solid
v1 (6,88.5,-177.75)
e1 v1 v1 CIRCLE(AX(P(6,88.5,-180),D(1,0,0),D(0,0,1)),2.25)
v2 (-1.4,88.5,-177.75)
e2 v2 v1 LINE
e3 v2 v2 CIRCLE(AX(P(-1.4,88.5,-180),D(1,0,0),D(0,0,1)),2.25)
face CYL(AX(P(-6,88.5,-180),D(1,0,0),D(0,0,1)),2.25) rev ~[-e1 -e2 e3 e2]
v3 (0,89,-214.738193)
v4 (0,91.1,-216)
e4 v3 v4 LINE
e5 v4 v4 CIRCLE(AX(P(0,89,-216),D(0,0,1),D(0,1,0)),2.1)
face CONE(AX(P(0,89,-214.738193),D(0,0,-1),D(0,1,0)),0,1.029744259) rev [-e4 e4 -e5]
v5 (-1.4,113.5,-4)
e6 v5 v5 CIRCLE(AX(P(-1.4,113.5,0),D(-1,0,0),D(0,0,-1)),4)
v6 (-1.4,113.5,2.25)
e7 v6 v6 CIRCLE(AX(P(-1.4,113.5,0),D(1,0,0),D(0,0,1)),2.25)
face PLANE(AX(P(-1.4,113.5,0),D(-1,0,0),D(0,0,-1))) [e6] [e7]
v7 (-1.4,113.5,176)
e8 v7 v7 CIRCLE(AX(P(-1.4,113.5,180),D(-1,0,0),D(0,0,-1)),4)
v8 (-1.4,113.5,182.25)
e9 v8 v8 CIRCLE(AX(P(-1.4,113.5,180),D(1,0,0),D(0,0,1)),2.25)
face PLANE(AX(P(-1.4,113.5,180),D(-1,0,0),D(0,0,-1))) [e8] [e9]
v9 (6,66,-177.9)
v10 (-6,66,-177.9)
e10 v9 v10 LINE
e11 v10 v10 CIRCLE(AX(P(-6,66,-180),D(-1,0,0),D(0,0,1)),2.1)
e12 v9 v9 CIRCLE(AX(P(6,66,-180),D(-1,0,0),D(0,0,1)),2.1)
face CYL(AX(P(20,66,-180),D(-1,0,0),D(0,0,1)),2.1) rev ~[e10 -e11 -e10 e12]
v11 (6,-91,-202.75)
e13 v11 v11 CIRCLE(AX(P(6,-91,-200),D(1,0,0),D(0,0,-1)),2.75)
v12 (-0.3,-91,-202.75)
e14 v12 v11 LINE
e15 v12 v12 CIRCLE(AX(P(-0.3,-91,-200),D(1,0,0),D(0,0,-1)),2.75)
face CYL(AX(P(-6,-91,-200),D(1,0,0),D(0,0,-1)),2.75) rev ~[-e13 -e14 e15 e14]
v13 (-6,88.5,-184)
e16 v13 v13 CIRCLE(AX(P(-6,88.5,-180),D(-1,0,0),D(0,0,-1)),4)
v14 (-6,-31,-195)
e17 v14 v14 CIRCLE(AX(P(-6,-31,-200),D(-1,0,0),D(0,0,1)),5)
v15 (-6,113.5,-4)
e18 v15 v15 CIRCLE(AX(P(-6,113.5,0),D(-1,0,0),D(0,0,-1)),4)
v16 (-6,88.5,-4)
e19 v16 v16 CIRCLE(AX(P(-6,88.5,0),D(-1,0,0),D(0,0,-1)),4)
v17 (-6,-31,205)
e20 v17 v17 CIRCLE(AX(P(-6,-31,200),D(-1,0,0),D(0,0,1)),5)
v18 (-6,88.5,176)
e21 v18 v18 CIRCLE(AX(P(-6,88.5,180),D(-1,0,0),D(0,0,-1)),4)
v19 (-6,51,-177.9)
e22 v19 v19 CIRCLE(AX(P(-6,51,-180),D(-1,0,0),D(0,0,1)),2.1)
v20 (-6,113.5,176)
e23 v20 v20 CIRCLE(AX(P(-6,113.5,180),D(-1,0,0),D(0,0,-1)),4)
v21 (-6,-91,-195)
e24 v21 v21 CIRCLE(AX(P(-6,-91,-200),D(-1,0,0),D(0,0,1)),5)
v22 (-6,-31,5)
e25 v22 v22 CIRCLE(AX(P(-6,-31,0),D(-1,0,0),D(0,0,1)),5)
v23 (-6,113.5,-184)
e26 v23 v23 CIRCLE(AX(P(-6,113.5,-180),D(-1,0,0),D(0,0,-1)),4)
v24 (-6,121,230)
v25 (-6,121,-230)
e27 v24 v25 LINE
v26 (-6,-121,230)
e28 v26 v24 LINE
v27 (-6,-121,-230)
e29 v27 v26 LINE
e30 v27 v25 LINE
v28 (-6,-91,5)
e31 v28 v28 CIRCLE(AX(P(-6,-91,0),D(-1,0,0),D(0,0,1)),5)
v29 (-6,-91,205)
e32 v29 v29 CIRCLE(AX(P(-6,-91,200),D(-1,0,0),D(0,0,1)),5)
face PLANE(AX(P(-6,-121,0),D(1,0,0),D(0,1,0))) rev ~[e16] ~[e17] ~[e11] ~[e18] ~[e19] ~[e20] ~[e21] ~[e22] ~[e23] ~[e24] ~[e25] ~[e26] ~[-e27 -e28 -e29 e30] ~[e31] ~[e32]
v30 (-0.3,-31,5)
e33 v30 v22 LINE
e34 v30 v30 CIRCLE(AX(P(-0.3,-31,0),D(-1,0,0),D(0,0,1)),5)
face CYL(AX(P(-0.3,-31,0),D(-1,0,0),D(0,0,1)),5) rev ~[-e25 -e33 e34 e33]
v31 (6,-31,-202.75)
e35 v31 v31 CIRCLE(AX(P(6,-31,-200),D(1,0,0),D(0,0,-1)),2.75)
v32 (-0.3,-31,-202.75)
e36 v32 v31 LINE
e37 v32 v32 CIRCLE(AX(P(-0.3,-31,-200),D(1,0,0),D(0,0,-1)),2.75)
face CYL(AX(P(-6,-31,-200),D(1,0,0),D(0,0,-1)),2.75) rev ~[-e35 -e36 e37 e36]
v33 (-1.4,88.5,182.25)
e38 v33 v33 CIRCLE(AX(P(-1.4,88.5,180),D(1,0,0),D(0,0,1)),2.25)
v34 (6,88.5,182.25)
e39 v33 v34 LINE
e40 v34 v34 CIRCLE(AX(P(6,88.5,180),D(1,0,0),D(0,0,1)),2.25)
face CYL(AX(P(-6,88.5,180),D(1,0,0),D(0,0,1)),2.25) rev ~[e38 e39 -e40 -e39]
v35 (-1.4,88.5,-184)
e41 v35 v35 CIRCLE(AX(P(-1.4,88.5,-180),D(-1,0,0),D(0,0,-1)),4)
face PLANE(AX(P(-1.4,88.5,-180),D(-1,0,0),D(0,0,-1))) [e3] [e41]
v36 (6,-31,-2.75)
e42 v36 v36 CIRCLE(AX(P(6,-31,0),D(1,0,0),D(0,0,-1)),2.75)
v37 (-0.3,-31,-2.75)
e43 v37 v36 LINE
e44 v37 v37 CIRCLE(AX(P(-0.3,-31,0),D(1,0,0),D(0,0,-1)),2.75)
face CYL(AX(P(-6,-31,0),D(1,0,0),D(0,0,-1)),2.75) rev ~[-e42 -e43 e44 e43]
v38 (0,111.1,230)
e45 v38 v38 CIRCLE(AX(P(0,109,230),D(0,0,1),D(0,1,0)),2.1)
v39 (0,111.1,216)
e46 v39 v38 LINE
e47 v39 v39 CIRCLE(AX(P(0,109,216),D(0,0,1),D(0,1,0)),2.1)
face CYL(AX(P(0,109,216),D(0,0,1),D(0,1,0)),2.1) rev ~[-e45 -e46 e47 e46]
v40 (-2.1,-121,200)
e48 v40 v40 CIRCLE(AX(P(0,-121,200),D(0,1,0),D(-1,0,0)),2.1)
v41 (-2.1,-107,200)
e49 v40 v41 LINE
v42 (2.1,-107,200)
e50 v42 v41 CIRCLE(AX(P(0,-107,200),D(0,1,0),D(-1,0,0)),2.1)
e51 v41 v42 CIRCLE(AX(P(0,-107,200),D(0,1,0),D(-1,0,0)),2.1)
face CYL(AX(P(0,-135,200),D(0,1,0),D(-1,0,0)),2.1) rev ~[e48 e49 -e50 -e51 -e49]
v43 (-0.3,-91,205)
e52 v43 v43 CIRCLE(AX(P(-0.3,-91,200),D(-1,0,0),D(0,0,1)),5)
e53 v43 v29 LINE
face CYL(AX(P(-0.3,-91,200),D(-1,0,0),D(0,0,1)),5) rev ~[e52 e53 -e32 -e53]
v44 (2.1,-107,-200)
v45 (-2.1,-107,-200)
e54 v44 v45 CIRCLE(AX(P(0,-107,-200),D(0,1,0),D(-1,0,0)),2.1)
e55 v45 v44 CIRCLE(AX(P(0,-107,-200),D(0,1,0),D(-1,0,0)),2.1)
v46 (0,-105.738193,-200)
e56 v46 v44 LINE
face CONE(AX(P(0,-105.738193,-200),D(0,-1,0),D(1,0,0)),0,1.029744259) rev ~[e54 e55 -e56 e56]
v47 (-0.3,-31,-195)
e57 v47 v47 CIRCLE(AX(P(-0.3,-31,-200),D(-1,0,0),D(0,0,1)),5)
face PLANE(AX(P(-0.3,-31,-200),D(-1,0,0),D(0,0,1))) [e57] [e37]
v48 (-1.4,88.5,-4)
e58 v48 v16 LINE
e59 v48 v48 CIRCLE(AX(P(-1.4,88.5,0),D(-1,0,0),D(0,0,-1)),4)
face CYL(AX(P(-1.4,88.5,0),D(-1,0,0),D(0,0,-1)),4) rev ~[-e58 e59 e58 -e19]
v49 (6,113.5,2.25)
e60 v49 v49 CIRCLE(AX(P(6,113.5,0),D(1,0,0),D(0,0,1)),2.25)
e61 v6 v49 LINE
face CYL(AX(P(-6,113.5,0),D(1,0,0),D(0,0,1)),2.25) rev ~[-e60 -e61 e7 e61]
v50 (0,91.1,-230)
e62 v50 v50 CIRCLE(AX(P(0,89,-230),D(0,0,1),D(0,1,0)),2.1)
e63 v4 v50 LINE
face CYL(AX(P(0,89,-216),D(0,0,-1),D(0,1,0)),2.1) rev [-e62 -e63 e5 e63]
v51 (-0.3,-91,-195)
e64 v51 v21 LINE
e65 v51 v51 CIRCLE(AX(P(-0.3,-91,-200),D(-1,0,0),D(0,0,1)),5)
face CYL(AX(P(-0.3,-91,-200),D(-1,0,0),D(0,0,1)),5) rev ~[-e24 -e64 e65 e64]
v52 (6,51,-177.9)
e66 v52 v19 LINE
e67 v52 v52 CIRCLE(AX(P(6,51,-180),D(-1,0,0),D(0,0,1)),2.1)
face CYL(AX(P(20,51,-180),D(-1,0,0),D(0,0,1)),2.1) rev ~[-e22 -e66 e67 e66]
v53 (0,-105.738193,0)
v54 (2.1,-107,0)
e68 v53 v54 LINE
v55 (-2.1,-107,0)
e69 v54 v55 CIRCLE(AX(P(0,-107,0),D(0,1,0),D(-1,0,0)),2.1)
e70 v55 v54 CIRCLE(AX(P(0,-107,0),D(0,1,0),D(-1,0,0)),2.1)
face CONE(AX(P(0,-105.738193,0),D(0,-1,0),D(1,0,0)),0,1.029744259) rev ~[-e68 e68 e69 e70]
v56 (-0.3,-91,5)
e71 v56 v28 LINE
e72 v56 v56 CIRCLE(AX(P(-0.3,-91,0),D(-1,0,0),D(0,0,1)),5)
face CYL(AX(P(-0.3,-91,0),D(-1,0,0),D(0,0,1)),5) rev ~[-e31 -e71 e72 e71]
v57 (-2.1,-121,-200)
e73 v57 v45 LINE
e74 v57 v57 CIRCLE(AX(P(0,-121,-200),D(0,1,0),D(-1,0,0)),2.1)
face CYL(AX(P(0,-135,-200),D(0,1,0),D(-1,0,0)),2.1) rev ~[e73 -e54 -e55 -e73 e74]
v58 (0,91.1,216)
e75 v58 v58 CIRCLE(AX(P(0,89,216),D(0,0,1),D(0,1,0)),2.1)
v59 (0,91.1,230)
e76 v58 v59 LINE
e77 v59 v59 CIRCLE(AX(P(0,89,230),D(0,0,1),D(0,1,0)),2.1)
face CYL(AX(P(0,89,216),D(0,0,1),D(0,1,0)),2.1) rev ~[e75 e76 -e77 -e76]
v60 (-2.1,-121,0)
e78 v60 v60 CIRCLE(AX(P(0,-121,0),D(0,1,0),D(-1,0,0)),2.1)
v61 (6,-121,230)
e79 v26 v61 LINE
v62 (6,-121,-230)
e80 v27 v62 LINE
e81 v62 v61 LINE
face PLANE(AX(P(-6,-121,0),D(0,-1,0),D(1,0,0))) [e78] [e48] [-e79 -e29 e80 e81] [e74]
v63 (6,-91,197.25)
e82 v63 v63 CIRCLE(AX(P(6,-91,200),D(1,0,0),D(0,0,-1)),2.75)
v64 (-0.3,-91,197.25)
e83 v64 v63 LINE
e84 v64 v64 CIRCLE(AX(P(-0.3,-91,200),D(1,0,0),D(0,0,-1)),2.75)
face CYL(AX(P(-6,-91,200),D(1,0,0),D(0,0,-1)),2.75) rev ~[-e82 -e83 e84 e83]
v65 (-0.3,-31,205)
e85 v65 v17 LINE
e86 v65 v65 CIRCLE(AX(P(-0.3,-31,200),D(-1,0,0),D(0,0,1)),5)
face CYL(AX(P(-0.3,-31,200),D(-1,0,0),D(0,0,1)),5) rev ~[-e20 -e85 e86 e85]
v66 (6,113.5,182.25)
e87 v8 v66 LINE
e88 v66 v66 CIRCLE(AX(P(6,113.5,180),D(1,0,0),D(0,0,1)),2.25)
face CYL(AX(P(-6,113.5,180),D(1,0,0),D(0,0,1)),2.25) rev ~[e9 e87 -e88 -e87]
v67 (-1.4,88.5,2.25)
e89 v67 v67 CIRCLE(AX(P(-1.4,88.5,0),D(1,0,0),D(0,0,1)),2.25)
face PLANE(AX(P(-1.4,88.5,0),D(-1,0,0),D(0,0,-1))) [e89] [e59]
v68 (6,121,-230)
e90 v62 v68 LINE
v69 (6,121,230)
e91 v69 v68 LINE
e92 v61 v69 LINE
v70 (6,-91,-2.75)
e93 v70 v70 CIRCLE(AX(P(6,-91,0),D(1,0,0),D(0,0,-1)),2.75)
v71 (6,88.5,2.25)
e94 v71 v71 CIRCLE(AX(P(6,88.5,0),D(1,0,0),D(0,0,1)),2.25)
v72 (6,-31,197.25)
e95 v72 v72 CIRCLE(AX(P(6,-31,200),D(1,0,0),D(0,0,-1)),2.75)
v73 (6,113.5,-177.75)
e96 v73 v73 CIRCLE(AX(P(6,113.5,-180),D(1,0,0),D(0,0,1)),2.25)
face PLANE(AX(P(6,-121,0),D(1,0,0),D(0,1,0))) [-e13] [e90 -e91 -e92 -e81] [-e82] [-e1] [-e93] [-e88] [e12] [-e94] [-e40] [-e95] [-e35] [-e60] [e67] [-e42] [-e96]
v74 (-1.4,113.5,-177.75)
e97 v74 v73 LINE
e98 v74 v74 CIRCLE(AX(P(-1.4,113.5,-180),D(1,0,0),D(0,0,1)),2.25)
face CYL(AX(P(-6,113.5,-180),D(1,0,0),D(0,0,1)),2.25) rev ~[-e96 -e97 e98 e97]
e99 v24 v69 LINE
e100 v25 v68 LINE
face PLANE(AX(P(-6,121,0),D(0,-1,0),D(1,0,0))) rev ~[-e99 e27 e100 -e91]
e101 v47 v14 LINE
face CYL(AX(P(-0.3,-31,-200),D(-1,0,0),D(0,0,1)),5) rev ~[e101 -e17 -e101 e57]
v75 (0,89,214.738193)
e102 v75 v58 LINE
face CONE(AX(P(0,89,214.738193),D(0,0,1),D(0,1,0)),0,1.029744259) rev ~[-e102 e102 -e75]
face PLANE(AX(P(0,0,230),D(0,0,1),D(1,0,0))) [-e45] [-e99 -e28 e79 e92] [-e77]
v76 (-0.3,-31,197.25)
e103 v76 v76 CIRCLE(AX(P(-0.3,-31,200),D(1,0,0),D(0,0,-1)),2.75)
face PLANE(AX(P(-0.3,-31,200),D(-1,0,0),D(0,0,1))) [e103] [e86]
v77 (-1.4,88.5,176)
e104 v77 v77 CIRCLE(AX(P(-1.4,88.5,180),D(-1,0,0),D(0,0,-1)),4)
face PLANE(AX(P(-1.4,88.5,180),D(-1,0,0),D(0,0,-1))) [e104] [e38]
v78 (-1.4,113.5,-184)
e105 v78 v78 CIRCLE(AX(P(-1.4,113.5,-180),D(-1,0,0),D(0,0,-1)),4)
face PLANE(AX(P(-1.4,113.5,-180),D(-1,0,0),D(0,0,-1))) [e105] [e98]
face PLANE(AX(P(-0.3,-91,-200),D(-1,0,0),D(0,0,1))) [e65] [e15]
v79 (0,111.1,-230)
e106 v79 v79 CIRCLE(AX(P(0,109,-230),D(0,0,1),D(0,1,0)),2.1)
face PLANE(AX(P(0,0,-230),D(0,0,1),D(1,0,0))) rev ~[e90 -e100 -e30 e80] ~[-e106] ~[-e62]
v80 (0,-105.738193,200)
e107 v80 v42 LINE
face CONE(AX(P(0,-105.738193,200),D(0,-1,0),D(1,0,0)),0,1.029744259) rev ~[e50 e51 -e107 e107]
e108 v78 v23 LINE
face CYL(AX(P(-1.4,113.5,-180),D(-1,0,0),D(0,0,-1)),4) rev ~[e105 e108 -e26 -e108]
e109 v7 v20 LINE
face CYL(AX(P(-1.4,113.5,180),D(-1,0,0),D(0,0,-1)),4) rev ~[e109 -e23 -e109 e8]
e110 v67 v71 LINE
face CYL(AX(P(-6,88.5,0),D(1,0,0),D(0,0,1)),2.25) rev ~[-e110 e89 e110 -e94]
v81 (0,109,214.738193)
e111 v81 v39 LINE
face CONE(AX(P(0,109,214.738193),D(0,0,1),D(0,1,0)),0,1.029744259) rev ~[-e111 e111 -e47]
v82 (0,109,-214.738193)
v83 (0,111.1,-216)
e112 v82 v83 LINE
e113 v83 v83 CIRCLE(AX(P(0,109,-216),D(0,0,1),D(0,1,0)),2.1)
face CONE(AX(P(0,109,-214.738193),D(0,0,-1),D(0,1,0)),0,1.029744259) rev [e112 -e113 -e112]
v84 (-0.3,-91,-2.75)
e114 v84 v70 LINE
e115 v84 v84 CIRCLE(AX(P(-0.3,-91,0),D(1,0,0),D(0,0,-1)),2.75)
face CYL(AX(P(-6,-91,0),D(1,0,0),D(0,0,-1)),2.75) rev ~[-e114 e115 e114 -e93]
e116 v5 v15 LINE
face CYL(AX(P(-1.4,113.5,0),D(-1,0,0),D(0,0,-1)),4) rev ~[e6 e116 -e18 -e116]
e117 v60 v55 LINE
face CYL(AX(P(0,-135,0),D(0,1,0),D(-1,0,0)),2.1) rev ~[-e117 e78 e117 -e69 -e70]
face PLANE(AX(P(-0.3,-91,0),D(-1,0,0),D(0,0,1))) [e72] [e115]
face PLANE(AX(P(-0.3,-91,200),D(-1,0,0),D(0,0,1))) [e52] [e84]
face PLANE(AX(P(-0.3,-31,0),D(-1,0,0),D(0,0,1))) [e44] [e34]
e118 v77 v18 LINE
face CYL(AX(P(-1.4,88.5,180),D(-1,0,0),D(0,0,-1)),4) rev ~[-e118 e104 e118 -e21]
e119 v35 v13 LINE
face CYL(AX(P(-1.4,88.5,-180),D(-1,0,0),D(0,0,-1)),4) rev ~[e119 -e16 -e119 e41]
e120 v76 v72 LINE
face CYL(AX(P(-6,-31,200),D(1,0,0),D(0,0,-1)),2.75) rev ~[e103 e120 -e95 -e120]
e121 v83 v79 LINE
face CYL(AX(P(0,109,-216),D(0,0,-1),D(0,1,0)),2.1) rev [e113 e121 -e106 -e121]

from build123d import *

# Parameters (mm, degrees)
SKETCH_1_W                  = 12
SKETCH_1_H                  = 242
EXTRUDE_1_DEPTH             = 230
HOLE_WIZARD_M5_1_D          = 4.2
HOLE_WIZARD_M5_1_DEPTH      = 14
HOLE_WIZARD_M5_1_TIP        = 1.2618073
HOLE_WIZARD_1_D             = 5.5
HOLE_WIZARD_1_DEPTH         = 14
HOLE_WIZARD_1_CBORE_D       = 10
HOLE_WIZARD_1_CBORE_DEPTH   = 5.7
HOLE_WIZARD_1_TIP           = 1.652366702
HOLE_WIZARD_2_D             = 4.5
HOLE_WIZARD_2_DEPTH         = 14
HOLE_WIZARD_2_CBORE_D       = 8
HOLE_WIZARD_2_CBORE_DEPTH   = 4.6
HOLE_WIZARD_2_TIP           = 1.351936393
HOLE_WIZARD_M5_2_AT_2_COUNT = 2
HOLE_WIZARD_M5_2_AT_2_PITCH = 20
HOLE_WIZARD_M5_3_D          = 4.2
HOLE_WIZARD_M5_3_DEPTH      = 14
HOLE_WIZARD_M5_3_TIP        = 1.2618073


with BuildPart() as part:
    # 草图1 → 凸台-拉伸1 (new, symmetric)
    with BuildSketch(Plane.XY):
        Rectangle(SKETCH_1_W, SKETCH_1_H)
    extrude(amount=EXTRUDE_1_DEPTH, both=True)

    # M5 螺纹孔1
    with Locations(Plane.XZ.offset(121)):
        with Locations((0, 200), (0, 0), (0, -200)):
            Hole(HOLE_WIZARD_M5_1_D / 2, depth=HOLE_WIZARD_M5_1_DEPTH)
            with Locations((0, 0, -(HOLE_WIZARD_M5_1_DEPTH + HOLE_WIZARD_M5_1_TIP / 2))):  # 118° drill point
                Cone(0, HOLE_WIZARD_M5_1_D / 2, HOLE_WIZARD_M5_1_TIP, mode=Mode.SUBTRACT)

    # 打孔尺寸(%根据)内六角圆柱头螺钉的类型1
    with Locations(Plane.ZY.offset(6)):
        with Locations((200, -31), (200, -91), (0, -31), (0, -91), (-200, -31), (-200, -91)):
            CounterBoreHole(HOLE_WIZARD_1_D / 2, HOLE_WIZARD_1_CBORE_D / 2, HOLE_WIZARD_1_CBORE_DEPTH, depth=HOLE_WIZARD_1_DEPTH)
            with Locations((0, 0, -(HOLE_WIZARD_1_DEPTH + HOLE_WIZARD_1_TIP / 2))):  # 118° drill point
                Cone(0, HOLE_WIZARD_1_D / 2, HOLE_WIZARD_1_TIP, mode=Mode.SUBTRACT)

    # 打孔尺寸(%根据)内六角圆柱头螺钉的类型2
    with Locations(Plane(origin=(-6, 0, 0), x_dir=(0, 0, -1), z_dir=(-1, 0, 0))):
        with Locations((180, -113.5), (180, -88.5), (0, -113.5), (0, -88.5), (-180, -113.5), (-180, -88.5)):
            CounterBoreHole(HOLE_WIZARD_2_D / 2, HOLE_WIZARD_2_CBORE_D / 2, HOLE_WIZARD_2_CBORE_DEPTH, depth=HOLE_WIZARD_2_DEPTH)
            with Locations((0, 0, -(HOLE_WIZARD_2_DEPTH + HOLE_WIZARD_2_TIP / 2))):  # 118° drill point
                Cone(0, HOLE_WIZARD_2_D / 2, HOLE_WIZARD_2_TIP, mode=Mode.SUBTRACT)

    # 草图8 → M5 螺纹孔2 (revolve, cut)
    with BuildSketch(Plane(origin=(0, 109, -230), x_dir=(0, 1, 0), z_dir=(1, 0, 0))):
        Polygon((0, 0), (0, 15.2618073), (2.1, 14), (2.1, 0), align=None)
    hole_wizard_m5_2 = revolve(axis=Axis((0, 109, -236.35), (0, 0, 1)), mode=Mode.SUBTRACT)

    # M5 螺纹孔2 at 2: M5 螺纹孔2 ×2
    with Locations(*[(0, -i * HOLE_WIZARD_M5_2_AT_2_PITCH, 0) for i in range(1, HOLE_WIZARD_M5_2_AT_2_COUNT)]):
        add(hole_wizard_m5_2, mode=Mode.SUBTRACT)

    # 镜向1: M5 螺纹孔2 across plane
    add(hole_wizard_m5_2.mirror(Plane.XY), mode=Mode.SUBTRACT)

    # 镜向1 copy 1 sketch → 镜向1 copy 1 (revolve, cut)
    with BuildSketch(Plane(origin=(0, 89, 230), x_dir=(0, 1, 0), z_dir=(1, 0, 0))):
        Polygon((0, 0), (0, -15.2618073), (2.1, -14), (2.1, 0), align=None)
    revolve(axis=Axis((0, 89, 236.35), (0, 0, 1)), mode=Mode.SUBTRACT)

    # M5 螺纹孔3
    with Locations(Plane(origin=(6, 0, 0), x_dir=(0, 0, -1), z_dir=(1, 0, 0))):
        with Locations((180, 66), (180, 51)):
            Hole(HOLE_WIZARD_M5_3_D / 2, depth=HOLE_WIZARD_M5_3_DEPTH)
            with Locations((0, 0, -(HOLE_WIZARD_M5_3_DEPTH + HOLE_WIZARD_M5_3_TIP / 2))):  # 118° drill point
                Cone(0, HOLE_WIZARD_M5_3_D / 2, HOLE_WIZARD_M5_3_TIP, mode=Mode.SUBTRACT)


solid = part.part
